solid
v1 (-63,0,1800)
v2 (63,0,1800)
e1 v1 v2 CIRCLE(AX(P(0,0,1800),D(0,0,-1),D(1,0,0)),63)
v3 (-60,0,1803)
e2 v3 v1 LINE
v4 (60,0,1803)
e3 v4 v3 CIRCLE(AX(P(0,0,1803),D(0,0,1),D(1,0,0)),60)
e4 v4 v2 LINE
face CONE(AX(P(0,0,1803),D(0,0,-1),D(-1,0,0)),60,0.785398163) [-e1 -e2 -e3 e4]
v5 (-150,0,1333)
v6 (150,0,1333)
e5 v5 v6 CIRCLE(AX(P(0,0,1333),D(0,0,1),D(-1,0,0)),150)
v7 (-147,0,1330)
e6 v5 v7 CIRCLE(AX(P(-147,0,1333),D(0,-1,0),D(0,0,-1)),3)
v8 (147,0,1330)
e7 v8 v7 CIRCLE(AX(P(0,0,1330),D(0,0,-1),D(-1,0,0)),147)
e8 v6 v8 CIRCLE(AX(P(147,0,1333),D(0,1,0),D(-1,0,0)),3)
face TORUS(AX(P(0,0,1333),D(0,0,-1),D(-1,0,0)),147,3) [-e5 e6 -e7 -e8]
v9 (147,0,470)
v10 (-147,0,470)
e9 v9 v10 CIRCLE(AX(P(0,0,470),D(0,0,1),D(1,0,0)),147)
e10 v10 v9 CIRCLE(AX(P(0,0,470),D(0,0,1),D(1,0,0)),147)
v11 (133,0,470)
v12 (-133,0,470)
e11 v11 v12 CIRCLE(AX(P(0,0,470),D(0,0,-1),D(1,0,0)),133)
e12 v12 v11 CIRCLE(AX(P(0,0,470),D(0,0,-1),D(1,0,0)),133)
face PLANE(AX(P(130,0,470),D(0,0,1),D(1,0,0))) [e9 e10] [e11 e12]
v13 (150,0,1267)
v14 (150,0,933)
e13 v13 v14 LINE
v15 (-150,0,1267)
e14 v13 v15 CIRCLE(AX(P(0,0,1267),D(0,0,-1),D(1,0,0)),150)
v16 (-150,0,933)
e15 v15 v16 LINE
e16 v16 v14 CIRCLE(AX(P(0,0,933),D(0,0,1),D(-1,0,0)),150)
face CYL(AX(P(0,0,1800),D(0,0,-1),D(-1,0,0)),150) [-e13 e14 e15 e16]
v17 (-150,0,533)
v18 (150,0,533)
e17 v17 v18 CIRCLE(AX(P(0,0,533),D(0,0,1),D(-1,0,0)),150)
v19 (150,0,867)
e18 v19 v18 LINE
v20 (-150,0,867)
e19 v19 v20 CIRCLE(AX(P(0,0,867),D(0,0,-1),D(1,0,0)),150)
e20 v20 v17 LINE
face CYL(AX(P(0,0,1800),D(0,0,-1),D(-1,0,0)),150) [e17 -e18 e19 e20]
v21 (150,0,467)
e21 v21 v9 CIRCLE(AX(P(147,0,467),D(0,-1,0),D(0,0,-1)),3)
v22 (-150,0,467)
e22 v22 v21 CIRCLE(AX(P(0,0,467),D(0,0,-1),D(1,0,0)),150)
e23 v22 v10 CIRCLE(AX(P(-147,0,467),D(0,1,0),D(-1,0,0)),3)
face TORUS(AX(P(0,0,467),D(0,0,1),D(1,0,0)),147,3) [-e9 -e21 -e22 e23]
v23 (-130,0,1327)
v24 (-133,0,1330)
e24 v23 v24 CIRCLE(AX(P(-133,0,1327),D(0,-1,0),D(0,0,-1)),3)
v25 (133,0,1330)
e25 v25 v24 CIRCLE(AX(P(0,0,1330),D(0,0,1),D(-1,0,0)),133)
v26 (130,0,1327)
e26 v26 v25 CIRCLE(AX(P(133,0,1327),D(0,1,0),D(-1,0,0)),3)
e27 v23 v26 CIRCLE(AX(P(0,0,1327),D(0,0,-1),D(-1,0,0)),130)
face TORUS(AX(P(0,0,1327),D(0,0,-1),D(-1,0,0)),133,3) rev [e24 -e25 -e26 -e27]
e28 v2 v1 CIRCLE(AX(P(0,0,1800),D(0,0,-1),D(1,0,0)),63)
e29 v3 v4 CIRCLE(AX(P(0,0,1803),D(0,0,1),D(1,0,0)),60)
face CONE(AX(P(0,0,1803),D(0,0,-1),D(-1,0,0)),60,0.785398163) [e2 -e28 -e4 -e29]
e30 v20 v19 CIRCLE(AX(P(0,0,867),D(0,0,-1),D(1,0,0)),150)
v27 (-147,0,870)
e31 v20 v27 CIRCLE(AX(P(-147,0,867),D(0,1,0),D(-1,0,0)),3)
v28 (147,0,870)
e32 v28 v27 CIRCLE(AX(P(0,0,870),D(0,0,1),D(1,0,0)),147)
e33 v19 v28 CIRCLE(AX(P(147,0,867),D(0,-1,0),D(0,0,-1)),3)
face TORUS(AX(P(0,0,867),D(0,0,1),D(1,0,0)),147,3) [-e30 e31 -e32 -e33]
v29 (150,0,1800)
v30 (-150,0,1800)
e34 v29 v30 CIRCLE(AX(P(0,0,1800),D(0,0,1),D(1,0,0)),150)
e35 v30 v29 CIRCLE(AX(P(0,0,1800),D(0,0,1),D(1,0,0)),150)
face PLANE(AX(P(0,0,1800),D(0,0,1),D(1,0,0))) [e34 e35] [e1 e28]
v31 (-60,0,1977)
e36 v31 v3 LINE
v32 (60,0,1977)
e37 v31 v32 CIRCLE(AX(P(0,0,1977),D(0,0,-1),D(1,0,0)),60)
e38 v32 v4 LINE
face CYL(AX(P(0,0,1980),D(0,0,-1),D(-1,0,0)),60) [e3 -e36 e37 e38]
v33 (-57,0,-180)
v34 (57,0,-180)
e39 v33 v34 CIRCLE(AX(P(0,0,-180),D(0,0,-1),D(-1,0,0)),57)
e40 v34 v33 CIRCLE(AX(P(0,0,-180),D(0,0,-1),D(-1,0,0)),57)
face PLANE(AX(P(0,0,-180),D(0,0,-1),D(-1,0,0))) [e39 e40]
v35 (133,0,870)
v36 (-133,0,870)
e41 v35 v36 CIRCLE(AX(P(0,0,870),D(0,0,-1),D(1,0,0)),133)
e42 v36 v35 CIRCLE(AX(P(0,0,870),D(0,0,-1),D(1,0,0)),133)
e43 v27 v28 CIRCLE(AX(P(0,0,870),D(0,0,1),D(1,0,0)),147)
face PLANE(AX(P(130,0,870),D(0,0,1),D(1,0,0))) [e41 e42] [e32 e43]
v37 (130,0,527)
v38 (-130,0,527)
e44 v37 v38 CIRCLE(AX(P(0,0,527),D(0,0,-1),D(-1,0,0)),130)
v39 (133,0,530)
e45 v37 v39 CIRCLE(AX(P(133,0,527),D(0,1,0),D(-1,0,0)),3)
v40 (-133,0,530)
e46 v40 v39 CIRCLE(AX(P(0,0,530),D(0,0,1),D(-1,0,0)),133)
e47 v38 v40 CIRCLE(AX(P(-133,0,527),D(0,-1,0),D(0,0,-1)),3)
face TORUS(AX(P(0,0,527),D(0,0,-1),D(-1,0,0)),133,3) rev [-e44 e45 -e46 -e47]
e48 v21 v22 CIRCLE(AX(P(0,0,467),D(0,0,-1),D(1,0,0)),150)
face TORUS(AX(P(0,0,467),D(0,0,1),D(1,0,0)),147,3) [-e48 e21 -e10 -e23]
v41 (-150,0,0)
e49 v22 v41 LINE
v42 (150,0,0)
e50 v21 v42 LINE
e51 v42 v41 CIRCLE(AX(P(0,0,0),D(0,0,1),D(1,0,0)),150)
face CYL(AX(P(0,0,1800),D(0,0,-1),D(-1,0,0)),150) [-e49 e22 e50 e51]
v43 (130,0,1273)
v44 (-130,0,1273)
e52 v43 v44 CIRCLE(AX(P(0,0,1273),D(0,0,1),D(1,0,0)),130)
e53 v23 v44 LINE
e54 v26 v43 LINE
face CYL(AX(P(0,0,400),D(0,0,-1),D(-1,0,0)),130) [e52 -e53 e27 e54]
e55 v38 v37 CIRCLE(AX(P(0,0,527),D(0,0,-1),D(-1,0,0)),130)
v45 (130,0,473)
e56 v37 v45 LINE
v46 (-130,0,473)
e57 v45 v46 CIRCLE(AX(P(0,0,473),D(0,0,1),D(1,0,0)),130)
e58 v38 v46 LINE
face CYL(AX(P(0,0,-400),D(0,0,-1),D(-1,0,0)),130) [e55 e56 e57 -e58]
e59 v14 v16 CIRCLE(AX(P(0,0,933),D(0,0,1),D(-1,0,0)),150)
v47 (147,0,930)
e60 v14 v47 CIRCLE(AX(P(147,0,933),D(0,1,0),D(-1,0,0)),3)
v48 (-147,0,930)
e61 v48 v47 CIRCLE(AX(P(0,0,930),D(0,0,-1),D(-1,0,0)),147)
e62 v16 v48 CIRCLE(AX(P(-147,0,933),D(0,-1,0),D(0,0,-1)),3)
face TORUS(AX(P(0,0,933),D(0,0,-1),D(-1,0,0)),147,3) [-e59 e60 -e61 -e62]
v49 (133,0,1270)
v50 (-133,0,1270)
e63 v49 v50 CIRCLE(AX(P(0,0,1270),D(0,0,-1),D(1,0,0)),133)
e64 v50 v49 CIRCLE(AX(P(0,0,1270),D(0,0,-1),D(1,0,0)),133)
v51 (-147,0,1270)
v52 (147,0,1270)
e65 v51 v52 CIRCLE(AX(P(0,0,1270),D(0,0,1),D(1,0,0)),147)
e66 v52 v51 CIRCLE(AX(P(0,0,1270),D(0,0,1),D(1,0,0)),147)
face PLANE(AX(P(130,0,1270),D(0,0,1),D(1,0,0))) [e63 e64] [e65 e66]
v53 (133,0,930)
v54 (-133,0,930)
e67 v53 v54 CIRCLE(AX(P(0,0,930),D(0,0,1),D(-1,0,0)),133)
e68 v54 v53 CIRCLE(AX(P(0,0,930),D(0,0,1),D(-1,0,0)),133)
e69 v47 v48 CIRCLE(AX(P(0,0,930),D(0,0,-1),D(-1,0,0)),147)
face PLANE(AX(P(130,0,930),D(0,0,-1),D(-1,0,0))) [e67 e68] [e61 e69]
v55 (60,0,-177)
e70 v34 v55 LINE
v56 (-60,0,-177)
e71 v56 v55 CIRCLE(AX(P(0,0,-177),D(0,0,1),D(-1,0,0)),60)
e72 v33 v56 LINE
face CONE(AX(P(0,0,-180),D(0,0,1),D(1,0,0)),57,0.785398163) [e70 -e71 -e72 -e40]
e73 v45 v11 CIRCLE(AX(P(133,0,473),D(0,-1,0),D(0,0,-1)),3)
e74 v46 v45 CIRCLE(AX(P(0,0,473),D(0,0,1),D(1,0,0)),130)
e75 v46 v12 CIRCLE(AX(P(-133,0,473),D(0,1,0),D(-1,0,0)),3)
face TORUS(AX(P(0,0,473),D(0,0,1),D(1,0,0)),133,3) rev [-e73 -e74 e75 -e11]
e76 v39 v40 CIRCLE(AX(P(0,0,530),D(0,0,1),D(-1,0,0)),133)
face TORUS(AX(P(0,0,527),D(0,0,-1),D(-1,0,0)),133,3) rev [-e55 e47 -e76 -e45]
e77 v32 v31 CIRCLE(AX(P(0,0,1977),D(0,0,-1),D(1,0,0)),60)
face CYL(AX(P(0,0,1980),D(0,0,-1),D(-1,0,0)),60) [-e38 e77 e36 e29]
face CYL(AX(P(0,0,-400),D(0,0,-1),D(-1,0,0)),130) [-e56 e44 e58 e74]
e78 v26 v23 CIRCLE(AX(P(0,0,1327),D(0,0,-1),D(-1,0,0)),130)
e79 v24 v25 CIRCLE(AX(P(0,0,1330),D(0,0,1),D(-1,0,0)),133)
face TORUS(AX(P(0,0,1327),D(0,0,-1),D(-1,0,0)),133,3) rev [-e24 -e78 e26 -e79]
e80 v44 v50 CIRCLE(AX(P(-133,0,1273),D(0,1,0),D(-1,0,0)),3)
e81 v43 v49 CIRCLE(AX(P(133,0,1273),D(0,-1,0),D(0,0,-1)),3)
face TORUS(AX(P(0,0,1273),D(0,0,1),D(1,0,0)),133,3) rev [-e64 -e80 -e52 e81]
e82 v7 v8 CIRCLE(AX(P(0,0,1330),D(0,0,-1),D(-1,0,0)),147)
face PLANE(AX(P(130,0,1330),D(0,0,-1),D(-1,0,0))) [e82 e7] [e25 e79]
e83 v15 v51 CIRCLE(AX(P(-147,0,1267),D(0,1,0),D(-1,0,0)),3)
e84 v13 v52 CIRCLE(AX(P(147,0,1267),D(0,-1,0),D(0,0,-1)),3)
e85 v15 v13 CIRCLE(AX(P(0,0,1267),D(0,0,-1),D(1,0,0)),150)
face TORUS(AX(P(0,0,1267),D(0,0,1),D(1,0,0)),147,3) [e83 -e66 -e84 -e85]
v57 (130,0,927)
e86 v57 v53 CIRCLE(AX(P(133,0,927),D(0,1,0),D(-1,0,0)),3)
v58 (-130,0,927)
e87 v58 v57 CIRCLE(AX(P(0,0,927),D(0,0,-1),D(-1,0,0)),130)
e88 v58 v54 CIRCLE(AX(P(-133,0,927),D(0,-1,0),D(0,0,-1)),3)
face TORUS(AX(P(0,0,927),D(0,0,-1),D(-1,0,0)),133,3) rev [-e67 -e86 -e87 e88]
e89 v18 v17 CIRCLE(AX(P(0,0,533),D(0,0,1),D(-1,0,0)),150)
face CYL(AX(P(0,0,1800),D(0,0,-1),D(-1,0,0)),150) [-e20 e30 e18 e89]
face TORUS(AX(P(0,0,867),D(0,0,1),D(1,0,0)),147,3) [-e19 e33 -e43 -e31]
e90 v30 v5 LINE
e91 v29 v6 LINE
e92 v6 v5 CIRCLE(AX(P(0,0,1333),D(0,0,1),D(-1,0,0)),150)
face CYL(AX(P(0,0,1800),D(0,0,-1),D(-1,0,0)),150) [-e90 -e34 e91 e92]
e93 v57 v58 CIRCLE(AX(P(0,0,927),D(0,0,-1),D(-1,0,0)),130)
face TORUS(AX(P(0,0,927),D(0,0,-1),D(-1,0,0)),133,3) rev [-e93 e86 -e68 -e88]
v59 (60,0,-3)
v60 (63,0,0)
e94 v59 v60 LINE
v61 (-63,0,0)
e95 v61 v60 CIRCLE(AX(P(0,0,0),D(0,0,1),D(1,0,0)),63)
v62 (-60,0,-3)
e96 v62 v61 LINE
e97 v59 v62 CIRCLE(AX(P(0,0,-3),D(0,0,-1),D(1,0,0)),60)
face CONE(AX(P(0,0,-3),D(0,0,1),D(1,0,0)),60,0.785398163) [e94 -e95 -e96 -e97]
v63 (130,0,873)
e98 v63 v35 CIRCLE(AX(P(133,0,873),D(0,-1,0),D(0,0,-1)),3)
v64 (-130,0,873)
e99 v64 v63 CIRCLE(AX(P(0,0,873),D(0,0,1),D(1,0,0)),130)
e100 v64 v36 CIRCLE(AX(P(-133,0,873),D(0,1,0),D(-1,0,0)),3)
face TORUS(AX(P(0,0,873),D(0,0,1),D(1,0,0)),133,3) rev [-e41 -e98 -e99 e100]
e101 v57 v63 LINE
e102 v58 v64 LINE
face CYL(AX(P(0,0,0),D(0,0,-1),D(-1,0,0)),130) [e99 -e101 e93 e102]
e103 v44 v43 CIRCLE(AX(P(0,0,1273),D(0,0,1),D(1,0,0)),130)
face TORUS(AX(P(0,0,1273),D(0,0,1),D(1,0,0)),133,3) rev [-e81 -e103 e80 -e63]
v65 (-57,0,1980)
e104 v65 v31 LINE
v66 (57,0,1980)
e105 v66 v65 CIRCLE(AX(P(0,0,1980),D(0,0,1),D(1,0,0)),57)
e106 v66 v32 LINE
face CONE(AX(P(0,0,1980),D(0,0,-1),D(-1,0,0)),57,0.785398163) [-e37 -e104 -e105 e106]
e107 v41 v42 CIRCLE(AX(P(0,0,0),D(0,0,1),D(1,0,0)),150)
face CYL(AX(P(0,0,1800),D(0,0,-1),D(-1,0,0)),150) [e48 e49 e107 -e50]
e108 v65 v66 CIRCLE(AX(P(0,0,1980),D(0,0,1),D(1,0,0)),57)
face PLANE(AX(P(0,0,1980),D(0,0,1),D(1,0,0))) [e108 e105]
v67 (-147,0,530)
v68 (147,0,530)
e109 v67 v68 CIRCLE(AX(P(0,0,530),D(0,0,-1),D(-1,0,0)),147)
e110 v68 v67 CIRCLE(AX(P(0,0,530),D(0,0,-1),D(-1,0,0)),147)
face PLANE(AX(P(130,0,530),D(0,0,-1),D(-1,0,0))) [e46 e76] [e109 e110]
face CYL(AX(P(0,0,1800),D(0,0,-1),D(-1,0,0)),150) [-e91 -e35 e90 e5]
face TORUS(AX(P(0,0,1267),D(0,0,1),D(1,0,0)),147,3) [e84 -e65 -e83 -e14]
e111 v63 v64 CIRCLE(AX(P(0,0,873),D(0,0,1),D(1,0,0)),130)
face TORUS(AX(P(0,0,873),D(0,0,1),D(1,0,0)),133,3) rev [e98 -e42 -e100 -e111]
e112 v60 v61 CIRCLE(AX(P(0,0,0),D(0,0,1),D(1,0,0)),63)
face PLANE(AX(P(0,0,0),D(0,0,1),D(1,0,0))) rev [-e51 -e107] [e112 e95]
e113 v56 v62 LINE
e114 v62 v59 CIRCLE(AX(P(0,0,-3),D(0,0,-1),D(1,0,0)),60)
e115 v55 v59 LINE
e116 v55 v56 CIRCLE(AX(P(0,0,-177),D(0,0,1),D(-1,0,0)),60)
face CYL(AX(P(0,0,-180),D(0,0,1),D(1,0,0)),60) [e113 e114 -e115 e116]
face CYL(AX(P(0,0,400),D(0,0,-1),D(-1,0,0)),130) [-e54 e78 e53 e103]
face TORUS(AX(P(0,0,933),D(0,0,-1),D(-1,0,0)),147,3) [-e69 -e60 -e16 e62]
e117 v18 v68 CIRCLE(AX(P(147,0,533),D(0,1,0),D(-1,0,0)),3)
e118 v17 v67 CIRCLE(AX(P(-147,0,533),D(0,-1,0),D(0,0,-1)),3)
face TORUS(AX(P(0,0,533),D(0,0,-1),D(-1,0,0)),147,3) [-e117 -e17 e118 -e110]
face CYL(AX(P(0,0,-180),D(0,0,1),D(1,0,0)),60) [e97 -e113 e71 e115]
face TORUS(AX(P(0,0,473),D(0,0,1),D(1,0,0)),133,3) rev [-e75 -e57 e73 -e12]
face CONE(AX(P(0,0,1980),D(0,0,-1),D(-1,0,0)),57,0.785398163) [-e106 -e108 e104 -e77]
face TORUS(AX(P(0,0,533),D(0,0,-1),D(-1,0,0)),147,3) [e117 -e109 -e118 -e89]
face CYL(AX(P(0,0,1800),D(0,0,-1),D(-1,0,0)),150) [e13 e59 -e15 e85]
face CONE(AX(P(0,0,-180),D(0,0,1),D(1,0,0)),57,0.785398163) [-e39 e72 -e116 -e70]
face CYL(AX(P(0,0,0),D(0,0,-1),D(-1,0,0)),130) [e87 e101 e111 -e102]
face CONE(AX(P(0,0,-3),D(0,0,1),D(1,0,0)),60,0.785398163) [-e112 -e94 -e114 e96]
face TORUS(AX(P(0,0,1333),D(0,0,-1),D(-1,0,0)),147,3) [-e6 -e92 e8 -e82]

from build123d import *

# Parameters (mm, degrees)
SKETCH1_R                  = 150
BOSS_EXTRUDE1_DEPTH        = 1800
SKETCH2_W                  = 40
SKETCH2_H                  = 60
FILLET1_R                  = 3
LPATTERN1_COUNT            = 2
LPATTERN1_PITCH            = 400
FILLET1_OF_LPATTERN1_R     = 3
LPATTERN1_COL_COUNT        = 2
LPATTERN1_COL_PITCH        = 400
FILLET1_OF_LPATTERN1_COL_R = 3
SKETCH3_R                  = 60
BOSS_EXTRUDE2_DEPTH        = 180
CHAMFER1_SIZE              = 3
BOSS_EXTRUDE3_START        = 180
SKETCH4_R                  = 60
BOSS_EXTRUDE3_DEPTH        = 180
CHAMFER2_SIZE              = 3


with BuildPart() as part:
    # Sketch1 → Boss-Extrude1 (new body)
    with BuildSketch(Plane.XY):
        Circle(SKETCH1_R)
    extrude(amount=BOSS_EXTRUDE1_DEPTH)

    # Sketch2 → Cut-Revolve1 (revolve, cut)
    with BuildSketch(Plane(origin=(0, 0, 0), x_dir=(1, 0, 0), z_dir=(0, 1, 0)), mode=Mode.PRIVATE) as cut_revolve1_sk:
        with Locations((150, -900)):
            Rectangle(SKETCH2_W, SKETCH2_H)
    cut_revolve1 = revolve(cut_revolve1_sk.sketch.rotate(Axis((0, 0, 0), (0, 0, 1)), 180), axis=Axis((0, 0, 0), (0, 0, 1)), mode=Mode.SUBTRACT)

    # Fillet1
    fillet1_edges = [part.edges().sort_by_distance(p)[0] for p in [
        (130, 0, 930),
        (-150, 0, 930),
        (130, 0, 870),
        (-150, 0, 870),
    ]]
    fillet(fillet1_edges, radius=FILLET1_R)

    # LPattern1: Cut-Revolve1 ×2
    with Locations(*[(0, 0, -i * LPATTERN1_PITCH) for i in range(1, LPATTERN1_COUNT)]):
        add(cut_revolve1, mode=Mode.SUBTRACT)

    # Fillet1 of LPattern1
    fillet1_of_lpattern1_edges = [part.edges().sort_by_distance(p)[0] for p in [
        (130, 0, 530),
        (-150, 0, 530),
        (130, 0, 470),
        (-150, 0, 470),
    ]]
    fillet(fillet1_of_lpattern1_edges, radius=FILLET1_OF_LPATTERN1_R)

    # LPattern1 col: Cut-Revolve1 ×2
    with Locations(*[(0, 0, i * LPATTERN1_COL_PITCH) for i in range(1, LPATTERN1_COL_COUNT)]):
        add(cut_revolve1, mode=Mode.SUBTRACT)

    # Fillet1 of LPattern1 col
    fillet1_of_lpattern1_col_edges = [part.edges().sort_by_distance(p)[0] for p in [
        (130, 0, 1330),
        (-150, 0, 1330),
        (130, 0, 1270),
        (-150, 0, 1270),
    ]]
    fillet(fillet1_of_lpattern1_col_edges, radius=FILLET1_OF_LPATTERN1_COL_R)

    # Sketch3 → Boss-Extrude2 (add)
    with BuildSketch(Plane.XY.offset(1800)):
        Circle(SKETCH3_R)
    extrude(amount=BOSS_EXTRUDE2_DEPTH)

    # Chamfer1
    chamfer1_edges = [part.edges().sort_by_distance(p)[0] for p in [
        (-60, 0, 1800),
        (-60, 0, 1980),
    ]]
    chamfer(chamfer1_edges, length=CHAMFER1_SIZE)

    # Sketch4 → Boss-Extrude3 (add)
    with BuildSketch(Plane(origin=(0, 0, 0), x_dir=(-1, 0, 0), z_dir=(0, 0, -1)).offset(BOSS_EXTRUDE3_START)):
        with Locations(Location((0, 0, 0), (0, 0, 180))):
            Circle(SKETCH4_R)
    extrude(amount=-BOSS_EXTRUDE3_DEPTH)

    # Chamfer2
    chamfer2_edges = [part.edges().sort_by_distance(p)[0] for p in [
        (-60, 0, 0),
        (-60, 0, -180),
    ]]
    chamfer(chamfer2_edges, length=CHAMFER2_SIZE)


solid = part.part
